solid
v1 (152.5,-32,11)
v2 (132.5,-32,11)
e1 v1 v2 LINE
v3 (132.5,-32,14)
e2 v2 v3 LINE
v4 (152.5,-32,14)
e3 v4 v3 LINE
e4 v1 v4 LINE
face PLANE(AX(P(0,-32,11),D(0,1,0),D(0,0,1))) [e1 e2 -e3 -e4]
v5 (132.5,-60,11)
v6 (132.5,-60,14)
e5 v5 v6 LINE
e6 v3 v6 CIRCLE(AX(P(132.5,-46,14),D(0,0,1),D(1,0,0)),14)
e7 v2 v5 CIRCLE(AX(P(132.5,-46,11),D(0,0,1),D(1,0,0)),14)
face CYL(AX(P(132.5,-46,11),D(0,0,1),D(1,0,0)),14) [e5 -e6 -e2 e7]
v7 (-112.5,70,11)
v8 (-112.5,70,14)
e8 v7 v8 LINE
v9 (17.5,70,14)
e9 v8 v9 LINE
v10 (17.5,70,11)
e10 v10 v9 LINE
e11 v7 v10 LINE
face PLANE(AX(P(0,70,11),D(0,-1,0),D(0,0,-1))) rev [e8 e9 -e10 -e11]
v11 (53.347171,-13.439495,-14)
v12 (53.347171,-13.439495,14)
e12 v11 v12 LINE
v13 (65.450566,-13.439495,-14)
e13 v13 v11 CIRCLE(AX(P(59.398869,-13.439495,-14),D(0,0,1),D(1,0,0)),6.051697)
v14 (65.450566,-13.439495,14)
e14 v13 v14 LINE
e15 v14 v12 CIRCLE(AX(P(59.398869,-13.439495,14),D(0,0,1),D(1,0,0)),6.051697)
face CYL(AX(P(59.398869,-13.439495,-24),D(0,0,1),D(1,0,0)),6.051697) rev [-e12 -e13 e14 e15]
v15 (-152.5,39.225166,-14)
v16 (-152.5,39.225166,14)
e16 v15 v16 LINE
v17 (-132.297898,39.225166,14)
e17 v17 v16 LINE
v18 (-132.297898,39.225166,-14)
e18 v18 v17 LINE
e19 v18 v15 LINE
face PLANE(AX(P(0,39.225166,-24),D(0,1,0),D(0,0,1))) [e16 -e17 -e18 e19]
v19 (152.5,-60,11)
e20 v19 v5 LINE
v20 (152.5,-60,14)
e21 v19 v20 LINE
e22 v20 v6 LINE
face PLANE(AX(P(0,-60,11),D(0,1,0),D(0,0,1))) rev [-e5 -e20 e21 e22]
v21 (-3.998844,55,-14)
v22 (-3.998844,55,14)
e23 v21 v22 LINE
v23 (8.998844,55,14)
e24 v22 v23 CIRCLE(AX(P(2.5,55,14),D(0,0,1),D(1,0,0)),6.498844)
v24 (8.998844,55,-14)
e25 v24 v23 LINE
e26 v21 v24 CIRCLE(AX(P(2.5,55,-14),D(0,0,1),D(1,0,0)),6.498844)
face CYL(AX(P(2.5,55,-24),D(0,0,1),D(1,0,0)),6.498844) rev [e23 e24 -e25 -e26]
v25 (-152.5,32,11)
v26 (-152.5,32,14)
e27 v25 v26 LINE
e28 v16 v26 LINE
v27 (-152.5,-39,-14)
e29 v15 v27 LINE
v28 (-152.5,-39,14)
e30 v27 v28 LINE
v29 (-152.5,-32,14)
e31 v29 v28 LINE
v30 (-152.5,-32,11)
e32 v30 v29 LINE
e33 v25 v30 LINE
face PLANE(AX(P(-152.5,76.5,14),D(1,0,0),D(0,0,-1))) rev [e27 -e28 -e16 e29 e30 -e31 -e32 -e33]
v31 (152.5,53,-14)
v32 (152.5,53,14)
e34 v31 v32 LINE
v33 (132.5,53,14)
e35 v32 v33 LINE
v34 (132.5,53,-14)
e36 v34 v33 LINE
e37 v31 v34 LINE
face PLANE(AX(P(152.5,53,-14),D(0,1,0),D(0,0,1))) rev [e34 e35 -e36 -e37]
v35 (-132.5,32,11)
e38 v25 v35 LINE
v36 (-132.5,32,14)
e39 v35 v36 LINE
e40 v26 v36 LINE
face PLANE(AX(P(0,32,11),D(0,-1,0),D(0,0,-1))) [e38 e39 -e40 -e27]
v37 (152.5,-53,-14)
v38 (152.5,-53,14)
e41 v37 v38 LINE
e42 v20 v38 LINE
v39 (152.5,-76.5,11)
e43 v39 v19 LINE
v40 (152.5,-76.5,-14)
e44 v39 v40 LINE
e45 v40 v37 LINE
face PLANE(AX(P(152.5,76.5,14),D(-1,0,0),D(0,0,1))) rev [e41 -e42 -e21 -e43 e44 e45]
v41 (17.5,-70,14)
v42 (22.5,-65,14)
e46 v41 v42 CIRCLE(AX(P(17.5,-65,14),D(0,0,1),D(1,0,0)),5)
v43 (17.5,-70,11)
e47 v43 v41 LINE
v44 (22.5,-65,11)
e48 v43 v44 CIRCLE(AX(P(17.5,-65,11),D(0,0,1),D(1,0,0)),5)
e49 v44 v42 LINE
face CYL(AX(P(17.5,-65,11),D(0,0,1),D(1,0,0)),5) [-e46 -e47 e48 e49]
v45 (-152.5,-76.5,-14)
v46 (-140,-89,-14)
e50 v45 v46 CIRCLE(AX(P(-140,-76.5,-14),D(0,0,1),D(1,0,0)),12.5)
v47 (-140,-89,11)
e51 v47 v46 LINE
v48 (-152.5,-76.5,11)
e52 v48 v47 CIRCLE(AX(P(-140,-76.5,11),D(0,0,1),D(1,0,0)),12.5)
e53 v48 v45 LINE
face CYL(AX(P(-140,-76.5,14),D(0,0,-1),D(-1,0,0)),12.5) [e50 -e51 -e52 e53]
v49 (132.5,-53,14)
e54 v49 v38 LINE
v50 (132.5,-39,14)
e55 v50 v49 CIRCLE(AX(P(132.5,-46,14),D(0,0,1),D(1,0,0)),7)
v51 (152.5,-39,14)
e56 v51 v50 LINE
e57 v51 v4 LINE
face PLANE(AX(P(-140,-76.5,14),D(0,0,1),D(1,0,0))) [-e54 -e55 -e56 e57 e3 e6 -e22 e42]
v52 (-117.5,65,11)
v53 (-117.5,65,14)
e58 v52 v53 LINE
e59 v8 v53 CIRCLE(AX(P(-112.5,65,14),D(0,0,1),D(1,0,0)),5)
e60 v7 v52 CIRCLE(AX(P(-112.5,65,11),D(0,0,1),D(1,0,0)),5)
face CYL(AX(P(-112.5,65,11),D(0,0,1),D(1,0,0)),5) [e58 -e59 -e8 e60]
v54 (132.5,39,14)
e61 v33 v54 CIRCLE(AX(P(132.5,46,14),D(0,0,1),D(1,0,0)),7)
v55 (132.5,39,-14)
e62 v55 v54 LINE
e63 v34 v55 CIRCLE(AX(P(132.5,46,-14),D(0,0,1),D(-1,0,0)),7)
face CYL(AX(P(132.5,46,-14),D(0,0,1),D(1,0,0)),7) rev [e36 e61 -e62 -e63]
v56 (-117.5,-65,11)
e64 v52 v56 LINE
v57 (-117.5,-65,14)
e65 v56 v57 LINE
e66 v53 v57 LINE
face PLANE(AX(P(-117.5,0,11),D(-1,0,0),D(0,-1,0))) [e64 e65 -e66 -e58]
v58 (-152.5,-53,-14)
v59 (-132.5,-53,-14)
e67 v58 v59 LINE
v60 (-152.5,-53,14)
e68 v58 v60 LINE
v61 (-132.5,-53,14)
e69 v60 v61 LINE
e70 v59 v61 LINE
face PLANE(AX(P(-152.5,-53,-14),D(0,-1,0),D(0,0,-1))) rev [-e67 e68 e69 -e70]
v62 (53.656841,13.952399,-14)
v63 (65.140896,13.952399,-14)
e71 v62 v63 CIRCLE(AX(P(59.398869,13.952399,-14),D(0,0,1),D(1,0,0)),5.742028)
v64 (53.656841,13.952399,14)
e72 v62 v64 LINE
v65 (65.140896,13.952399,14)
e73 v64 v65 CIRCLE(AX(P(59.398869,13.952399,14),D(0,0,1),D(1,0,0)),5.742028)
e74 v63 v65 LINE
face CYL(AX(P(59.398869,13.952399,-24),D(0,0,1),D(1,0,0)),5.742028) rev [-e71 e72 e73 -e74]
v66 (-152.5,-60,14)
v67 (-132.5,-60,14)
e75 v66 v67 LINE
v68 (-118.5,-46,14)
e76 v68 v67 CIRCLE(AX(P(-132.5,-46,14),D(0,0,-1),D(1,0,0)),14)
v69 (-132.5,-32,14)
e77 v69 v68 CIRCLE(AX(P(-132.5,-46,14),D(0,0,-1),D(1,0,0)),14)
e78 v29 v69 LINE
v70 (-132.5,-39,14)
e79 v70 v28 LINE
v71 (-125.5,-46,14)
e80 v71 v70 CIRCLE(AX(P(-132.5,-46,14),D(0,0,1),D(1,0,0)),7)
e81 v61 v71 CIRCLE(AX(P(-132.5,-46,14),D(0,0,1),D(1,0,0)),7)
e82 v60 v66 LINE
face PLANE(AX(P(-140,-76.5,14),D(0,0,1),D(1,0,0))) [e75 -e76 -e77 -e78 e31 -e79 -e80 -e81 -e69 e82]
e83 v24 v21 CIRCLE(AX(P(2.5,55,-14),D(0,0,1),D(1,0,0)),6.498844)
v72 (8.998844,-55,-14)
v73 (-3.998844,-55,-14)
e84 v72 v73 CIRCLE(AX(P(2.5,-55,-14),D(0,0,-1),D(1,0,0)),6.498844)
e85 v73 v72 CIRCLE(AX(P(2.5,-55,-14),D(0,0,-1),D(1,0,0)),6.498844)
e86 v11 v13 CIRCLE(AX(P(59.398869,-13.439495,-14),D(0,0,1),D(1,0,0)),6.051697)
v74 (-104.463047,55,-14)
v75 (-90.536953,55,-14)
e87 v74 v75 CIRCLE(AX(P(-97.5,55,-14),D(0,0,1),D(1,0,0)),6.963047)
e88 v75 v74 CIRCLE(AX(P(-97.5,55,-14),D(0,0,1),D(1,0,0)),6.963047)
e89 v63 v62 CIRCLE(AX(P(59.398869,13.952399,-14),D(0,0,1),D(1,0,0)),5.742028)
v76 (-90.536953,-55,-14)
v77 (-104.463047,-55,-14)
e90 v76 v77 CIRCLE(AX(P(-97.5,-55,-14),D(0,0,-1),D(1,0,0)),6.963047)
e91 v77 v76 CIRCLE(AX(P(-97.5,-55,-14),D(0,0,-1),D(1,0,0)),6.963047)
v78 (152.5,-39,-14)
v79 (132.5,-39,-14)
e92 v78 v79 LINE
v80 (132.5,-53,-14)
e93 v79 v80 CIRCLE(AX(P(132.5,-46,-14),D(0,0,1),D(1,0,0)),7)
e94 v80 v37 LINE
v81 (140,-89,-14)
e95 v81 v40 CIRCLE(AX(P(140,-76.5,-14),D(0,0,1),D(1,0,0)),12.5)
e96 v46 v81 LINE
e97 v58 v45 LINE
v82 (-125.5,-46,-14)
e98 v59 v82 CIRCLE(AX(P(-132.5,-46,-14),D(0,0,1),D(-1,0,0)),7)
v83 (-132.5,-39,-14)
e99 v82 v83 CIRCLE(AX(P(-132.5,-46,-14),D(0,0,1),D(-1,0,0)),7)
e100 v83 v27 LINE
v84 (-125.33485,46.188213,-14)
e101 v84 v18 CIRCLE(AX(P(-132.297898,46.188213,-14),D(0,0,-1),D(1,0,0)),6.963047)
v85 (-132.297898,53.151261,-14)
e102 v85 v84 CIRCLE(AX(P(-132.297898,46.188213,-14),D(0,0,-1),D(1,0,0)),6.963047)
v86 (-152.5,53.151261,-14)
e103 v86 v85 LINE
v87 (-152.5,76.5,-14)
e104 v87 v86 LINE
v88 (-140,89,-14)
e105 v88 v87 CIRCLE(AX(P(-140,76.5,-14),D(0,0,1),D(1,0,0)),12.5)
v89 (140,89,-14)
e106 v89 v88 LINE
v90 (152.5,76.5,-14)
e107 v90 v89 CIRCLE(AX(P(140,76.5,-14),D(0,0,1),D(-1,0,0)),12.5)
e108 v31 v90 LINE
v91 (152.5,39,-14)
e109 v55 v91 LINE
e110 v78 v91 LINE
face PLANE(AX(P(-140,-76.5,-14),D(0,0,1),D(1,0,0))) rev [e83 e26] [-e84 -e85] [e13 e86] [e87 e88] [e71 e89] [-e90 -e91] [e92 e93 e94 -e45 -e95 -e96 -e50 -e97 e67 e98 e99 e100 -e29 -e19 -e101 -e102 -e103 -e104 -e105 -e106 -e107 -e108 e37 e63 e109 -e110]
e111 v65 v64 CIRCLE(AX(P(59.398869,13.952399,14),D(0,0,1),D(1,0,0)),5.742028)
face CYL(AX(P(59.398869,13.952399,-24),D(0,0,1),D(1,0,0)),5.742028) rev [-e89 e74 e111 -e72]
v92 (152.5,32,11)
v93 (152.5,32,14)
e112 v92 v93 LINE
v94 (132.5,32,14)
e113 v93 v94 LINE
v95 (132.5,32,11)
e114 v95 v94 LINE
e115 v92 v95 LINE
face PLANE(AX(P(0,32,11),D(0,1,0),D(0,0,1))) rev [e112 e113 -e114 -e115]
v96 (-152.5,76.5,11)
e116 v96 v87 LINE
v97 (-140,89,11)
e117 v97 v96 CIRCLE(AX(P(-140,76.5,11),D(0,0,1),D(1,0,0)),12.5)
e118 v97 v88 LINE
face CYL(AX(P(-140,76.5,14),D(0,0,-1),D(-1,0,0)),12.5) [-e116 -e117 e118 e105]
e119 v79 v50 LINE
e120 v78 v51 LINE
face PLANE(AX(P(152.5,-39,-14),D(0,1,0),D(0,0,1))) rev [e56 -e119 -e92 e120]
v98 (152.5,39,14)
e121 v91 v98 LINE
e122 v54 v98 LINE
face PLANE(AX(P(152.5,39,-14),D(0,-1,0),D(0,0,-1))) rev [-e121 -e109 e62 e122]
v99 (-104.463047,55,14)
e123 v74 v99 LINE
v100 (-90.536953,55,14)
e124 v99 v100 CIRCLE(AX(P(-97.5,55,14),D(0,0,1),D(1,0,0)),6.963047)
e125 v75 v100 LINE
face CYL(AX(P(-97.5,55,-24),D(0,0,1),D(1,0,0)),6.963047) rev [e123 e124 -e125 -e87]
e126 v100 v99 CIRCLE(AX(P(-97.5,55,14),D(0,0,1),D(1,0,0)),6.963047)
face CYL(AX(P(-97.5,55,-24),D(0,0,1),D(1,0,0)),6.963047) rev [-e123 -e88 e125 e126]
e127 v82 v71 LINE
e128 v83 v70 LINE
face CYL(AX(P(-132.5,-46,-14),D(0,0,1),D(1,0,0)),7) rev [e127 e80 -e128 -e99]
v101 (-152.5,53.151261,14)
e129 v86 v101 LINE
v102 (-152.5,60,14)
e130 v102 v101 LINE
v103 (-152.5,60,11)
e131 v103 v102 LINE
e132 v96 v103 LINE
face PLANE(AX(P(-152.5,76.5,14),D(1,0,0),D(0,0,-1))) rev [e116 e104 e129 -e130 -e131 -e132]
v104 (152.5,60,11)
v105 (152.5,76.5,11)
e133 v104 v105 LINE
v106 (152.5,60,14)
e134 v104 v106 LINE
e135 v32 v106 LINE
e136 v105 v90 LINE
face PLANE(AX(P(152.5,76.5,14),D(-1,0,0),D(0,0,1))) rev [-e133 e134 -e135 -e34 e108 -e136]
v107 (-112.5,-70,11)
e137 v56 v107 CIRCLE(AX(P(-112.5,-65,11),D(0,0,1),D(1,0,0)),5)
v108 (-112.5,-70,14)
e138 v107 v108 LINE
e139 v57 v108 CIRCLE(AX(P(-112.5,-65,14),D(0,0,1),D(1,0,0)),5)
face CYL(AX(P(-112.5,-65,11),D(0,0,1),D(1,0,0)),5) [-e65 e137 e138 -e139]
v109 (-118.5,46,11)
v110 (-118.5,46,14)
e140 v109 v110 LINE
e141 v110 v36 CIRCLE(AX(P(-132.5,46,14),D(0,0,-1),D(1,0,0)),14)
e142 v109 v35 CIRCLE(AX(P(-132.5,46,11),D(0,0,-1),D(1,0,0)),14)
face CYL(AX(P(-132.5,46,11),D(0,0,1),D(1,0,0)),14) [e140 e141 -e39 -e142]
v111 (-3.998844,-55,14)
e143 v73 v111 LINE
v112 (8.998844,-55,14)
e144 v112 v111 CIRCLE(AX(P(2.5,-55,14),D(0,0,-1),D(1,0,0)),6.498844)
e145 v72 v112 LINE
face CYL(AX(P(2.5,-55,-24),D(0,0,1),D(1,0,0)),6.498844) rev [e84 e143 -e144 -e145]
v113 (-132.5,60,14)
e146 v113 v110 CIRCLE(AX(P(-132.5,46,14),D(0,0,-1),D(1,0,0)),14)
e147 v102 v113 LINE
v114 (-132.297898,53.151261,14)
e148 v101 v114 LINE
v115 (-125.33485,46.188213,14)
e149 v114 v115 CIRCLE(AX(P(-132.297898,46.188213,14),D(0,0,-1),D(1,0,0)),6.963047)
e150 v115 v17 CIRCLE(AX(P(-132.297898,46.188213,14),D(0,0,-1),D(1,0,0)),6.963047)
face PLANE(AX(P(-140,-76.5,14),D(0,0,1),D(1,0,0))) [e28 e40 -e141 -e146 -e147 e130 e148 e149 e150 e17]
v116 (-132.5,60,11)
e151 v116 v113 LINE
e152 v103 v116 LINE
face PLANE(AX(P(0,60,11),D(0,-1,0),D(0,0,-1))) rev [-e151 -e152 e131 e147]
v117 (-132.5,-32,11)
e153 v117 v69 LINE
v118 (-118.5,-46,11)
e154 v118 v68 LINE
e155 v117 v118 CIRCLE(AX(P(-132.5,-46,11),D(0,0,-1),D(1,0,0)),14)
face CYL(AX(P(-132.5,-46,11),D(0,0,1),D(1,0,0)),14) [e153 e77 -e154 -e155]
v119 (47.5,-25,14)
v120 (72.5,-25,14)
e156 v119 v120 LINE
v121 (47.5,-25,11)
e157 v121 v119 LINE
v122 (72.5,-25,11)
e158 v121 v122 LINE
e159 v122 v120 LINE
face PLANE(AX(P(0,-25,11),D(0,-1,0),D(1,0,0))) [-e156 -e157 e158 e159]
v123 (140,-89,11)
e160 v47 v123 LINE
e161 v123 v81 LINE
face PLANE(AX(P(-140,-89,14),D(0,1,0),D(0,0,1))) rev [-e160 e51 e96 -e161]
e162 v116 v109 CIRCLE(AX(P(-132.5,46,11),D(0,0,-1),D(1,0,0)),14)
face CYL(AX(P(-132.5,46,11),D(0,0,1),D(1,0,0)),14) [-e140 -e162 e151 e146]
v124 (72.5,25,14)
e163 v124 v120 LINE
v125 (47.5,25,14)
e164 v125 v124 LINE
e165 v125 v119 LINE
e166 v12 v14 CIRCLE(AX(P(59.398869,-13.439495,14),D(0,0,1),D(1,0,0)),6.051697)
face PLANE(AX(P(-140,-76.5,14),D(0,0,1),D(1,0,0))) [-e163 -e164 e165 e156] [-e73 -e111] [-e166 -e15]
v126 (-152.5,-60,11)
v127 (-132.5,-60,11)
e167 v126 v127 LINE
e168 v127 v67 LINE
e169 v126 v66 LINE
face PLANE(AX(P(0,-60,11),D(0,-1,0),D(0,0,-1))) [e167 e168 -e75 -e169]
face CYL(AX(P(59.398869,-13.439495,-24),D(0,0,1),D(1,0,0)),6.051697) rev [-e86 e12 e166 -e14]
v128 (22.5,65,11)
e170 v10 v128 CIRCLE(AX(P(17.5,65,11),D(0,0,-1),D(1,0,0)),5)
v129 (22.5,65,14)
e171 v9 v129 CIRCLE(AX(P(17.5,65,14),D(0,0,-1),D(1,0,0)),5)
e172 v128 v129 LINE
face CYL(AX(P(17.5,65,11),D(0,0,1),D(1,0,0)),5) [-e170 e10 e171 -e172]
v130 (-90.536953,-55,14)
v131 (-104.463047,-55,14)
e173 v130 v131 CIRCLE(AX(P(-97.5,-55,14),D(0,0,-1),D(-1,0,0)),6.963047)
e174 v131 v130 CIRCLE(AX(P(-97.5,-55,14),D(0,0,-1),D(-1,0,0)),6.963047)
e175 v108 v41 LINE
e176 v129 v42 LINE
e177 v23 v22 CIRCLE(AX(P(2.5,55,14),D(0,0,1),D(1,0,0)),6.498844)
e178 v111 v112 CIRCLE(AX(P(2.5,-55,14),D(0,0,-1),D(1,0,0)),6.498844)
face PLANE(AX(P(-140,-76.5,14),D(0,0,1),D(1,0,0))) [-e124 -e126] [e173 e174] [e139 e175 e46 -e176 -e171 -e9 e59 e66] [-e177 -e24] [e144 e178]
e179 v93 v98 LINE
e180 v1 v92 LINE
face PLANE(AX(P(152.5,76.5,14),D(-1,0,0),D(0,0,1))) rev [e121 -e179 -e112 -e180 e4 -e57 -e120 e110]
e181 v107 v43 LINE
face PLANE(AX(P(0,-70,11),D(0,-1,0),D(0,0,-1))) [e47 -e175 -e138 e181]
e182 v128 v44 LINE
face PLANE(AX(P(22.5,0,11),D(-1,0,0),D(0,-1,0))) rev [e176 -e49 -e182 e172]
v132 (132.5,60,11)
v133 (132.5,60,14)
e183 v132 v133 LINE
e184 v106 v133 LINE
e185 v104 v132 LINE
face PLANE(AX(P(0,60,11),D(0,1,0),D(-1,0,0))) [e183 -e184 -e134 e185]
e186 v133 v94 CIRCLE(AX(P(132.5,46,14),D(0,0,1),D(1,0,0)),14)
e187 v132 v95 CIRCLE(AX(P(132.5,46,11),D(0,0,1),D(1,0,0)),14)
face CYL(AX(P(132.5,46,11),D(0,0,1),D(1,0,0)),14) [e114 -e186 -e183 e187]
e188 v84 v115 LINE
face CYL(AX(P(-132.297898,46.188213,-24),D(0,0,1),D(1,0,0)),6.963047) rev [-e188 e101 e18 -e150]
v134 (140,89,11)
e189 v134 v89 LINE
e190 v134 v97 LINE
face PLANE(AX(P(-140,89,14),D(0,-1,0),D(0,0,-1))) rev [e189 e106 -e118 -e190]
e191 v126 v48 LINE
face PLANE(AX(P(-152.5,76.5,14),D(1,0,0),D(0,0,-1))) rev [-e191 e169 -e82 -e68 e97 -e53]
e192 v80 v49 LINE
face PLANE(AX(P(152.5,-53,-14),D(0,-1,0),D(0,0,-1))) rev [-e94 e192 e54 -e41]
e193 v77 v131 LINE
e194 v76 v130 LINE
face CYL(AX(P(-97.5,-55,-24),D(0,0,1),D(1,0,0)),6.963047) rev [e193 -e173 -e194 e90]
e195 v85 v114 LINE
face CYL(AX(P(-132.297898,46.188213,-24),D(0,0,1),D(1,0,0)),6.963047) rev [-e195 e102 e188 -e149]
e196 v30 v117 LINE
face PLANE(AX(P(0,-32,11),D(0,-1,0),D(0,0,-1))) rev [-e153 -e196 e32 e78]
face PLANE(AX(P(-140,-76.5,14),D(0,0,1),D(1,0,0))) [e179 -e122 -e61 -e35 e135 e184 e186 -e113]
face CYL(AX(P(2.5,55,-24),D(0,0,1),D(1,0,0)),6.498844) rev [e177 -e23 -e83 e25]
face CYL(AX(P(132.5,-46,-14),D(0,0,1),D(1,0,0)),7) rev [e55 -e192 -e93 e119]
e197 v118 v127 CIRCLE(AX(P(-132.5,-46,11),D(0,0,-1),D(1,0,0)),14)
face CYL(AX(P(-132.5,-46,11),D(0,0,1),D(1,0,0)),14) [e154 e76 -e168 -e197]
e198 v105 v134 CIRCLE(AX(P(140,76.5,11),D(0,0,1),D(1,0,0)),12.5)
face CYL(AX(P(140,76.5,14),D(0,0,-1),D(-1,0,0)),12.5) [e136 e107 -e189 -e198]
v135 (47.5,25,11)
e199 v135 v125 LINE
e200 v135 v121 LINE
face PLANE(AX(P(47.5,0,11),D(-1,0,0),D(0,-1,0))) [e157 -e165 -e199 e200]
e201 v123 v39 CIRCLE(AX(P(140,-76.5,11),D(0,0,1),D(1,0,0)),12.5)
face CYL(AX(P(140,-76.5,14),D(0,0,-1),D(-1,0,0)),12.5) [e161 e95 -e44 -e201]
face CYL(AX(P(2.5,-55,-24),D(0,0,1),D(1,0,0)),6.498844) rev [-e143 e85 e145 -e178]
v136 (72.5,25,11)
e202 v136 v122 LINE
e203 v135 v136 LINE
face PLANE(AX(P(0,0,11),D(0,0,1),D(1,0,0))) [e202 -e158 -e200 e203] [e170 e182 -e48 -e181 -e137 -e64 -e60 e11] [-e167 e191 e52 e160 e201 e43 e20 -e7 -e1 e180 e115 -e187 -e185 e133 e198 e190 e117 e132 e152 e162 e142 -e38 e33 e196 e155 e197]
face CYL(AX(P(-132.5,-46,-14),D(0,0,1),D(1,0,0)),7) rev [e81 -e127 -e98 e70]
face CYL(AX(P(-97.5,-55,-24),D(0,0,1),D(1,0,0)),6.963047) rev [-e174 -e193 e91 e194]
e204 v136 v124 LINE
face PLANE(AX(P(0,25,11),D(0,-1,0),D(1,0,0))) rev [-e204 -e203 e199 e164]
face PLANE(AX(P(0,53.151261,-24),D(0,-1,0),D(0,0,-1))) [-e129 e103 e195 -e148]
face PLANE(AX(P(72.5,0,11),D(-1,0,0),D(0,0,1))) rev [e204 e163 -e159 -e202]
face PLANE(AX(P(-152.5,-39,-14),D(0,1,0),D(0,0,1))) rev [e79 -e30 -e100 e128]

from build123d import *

# Parameters (mm, degrees)
BASE_PLATE_305X178X28_DEPTH    = 14
FACE_RECESS_3MM_DEPTH          = 3
END_SLOTS_PROFILE_R            = 6.963047248
END_SLOTS_PROFILE_R_2          = 6.498844098
END_SLOTS_PROFILE_R_3          = 5.742027746
END_SLOTS_PROFILE_R_4          = 6.051697443
END_U_SLOTS_CUT_DEPTH          = 38
TWO_HOLE_POCKET_CUT_DEPTH      = 179.777095848
TWO_HOLE_POCKET_CUT_DEPTH_BACK = 179.777095848


with BuildPart() as part:
    # Base Plate Profile → Base Plate 305x178x28 (new, symmetric)
    with BuildSketch(Plane.XY):
        with BuildLine():
            Line((-140, 89), (140, 89))
            ThreePointArc((140, 89), (148.838834765, 85.338834765), (152.5, 76.5))
            Line((152.5, 76.5), (152.5, -76.5))
            ThreePointArc((152.5, -76.5), (148.838834765, -85.338834765), (140, -89))
            Line((140, -89), (-140, -89))
            ThreePointArc((-140, -89), (-148.838834765, -85.338834765), (-152.5, -76.5))
            Line((-152.5, -76.5), (-152.5, 76.5))
            ThreePointArc((-152.5, 76.5), (-148.838834765, 85.338834765), (-140, 89))
        make_face()
    extrude(amount=BASE_PLATE_305X178X28_DEPTH, both=True)

    # Face Recess Profile → Face Recess 3mm (cut)
    with BuildSketch(Plane.XY.offset(14)):
        with BuildLine():
            ThreePointArc((-152.5, -76.5), (-148.838834765, -85.338834765), (-140, -89))
            Line((-140, -89), (140, -89))
            ThreePointArc((140, -89), (148.838834765, -85.338834765), (152.5, -76.5))
            Line((152.5, -76.5), (152.5, -60))
            Line((152.5, -60), (132.5, -60))
            ThreePointArc((132.5, -60), (118.5, -46), (132.5, -32))
            Line((132.5, -32), (152.5, -32))
            Line((152.5, -32), (152.5, 32))
            Line((152.5, 32), (132.5, 32))
            ThreePointArc((132.5, 32), (118.5, 46), (132.5, 60))
            Line((132.5, 60), (152.5, 60))
            Line((152.5, 60), (152.5, 76.5))
            ThreePointArc((152.5, 76.5), (148.838834765, 85.338834765), (140, 89))
            Line((140, 89), (-140, 89))
            ThreePointArc((-140, 89), (-148.838834765, 85.338834765), (-152.5, 76.5))
            Line((-152.5, 76.5), (-152.5, 60))
            Line((-152.5, 60), (-132.5, 60))
            ThreePointArc((-132.5, 60), (-118.5, 46), (-132.5, 32))
            Line((-132.5, 32), (-152.5, 32))
            Line((-152.5, 32), (-152.5, -32))
            Line((-152.5, -32), (-132.5, -32))
            ThreePointArc((-132.5, -32), (-118.5, -46), (-132.5, -60))
            Line((-132.5, -60), (-152.5, -60))
            Line((-152.5, -60), (-152.5, -76.5))
        make_face()
        with BuildLine():
            ThreePointArc((-117.5, 65), (-116.035533906, 68.535533906), (-112.5, 70))
            Line((-112.5, 70), (17.5, 70))
            ThreePointArc((17.5, 70), (21.035533906, 68.535533906), (22.5, 65))
            Line((22.5, 65), (22.5, -65))
            ThreePointArc((22.5, -65), (21.035533906, -68.535533906), (17.5, -70))
            Line((17.5, -70), (-112.5, -70))
            ThreePointArc((-112.5, -70), (-116.035533906, -68.535533906), (-117.5, -65))
            Line((-117.5, -65), (-117.5, 65))
        make_face(mode=Mode.SUBTRACT)
        Polygon((47.5, -25), (47.5, 25), (72.5, 25), (72.5, -25), (60, -25), align=None, mode=Mode.SUBTRACT)
    extrude(amount=-FACE_RECESS_3MM_DEPTH, mode=Mode.SUBTRACT)

    # End Slots Profile → End U-Slots Cut (cut)
    with BuildSketch(Plane.XY.offset(14)):
        with BuildLine():
            Line((-132.297897709, 53.151260658), (-152.5, 53.151260658))
            Line((-152.5, 53.151260658), (-152.5, 39.225166163))
            Line((-152.5, 39.225166163), (-132.297897709, 39.225166163))
            ThreePointArc((-132.297897709, 39.225166163), (-125.334850461, 46.188213411), (-132.297897709, 53.151260658))
        make_face()
        with Locations((-97.5, 55)):
            Circle(END_SLOTS_PROFILE_R)
        with Locations((2.5, 55)):
            Circle(END_SLOTS_PROFILE_R_2)
        with Locations((2.5, -55)):
            Circle(END_SLOTS_PROFILE_R_2)
        with Locations((59.398868635, 13.95239873)):
            Circle(END_SLOTS_PROFILE_R_3)
        with Locations((-97.5, -55)):
            Circle(END_SLOTS_PROFILE_R)
        with Locations((59.398868635, -13.43949496)):
            Circle(END_SLOTS_PROFILE_R_4)
    extrude(amount=-END_U_SLOTS_CUT_DEPTH, mode=Mode.SUBTRACT)

    # Hole Pocket Profile → Two-Hole Pocket Cut (cut, two sides: drawn at the far end of the back side and taken through both)
    with BuildSketch(Plane.XY.offset(14).offset(-TWO_HOLE_POCKET_CUT_DEPTH_BACK)):
        with BuildLine():
            Line((-152.5, -39), (-132.5, -39))
            ThreePointArc((-132.5, -39), (-125.5, -46), (-132.5, -53))
            Line((-132.5, -53), (-152.5, -53))
            Line((-152.5, -53), (-152.5, -39))
        make_face()
        with BuildLine():
            Line((152.5, -39), (152.5, -53))
            Line((152.5, -53), (132.5, -53))
            ThreePointArc((132.5, -53), (125.5, -46), (132.5, -39))
            Line((132.5, -39), (152.5, -39))
        make_face()
        with BuildLine():
            Line((152.5, 39), (132.5, 39))
            ThreePointArc((132.5, 39), (125.5, 46), (132.5, 53))
            Line((132.5, 53), (152.5, 53))
            Line((152.5, 53), (152.5, 39))
        make_face()
    extrude(amount=TWO_HOLE_POCKET_CUT_DEPTH + TWO_HOLE_POCKET_CUT_DEPTH_BACK, mode=Mode.SUBTRACT)


solid = part.part
